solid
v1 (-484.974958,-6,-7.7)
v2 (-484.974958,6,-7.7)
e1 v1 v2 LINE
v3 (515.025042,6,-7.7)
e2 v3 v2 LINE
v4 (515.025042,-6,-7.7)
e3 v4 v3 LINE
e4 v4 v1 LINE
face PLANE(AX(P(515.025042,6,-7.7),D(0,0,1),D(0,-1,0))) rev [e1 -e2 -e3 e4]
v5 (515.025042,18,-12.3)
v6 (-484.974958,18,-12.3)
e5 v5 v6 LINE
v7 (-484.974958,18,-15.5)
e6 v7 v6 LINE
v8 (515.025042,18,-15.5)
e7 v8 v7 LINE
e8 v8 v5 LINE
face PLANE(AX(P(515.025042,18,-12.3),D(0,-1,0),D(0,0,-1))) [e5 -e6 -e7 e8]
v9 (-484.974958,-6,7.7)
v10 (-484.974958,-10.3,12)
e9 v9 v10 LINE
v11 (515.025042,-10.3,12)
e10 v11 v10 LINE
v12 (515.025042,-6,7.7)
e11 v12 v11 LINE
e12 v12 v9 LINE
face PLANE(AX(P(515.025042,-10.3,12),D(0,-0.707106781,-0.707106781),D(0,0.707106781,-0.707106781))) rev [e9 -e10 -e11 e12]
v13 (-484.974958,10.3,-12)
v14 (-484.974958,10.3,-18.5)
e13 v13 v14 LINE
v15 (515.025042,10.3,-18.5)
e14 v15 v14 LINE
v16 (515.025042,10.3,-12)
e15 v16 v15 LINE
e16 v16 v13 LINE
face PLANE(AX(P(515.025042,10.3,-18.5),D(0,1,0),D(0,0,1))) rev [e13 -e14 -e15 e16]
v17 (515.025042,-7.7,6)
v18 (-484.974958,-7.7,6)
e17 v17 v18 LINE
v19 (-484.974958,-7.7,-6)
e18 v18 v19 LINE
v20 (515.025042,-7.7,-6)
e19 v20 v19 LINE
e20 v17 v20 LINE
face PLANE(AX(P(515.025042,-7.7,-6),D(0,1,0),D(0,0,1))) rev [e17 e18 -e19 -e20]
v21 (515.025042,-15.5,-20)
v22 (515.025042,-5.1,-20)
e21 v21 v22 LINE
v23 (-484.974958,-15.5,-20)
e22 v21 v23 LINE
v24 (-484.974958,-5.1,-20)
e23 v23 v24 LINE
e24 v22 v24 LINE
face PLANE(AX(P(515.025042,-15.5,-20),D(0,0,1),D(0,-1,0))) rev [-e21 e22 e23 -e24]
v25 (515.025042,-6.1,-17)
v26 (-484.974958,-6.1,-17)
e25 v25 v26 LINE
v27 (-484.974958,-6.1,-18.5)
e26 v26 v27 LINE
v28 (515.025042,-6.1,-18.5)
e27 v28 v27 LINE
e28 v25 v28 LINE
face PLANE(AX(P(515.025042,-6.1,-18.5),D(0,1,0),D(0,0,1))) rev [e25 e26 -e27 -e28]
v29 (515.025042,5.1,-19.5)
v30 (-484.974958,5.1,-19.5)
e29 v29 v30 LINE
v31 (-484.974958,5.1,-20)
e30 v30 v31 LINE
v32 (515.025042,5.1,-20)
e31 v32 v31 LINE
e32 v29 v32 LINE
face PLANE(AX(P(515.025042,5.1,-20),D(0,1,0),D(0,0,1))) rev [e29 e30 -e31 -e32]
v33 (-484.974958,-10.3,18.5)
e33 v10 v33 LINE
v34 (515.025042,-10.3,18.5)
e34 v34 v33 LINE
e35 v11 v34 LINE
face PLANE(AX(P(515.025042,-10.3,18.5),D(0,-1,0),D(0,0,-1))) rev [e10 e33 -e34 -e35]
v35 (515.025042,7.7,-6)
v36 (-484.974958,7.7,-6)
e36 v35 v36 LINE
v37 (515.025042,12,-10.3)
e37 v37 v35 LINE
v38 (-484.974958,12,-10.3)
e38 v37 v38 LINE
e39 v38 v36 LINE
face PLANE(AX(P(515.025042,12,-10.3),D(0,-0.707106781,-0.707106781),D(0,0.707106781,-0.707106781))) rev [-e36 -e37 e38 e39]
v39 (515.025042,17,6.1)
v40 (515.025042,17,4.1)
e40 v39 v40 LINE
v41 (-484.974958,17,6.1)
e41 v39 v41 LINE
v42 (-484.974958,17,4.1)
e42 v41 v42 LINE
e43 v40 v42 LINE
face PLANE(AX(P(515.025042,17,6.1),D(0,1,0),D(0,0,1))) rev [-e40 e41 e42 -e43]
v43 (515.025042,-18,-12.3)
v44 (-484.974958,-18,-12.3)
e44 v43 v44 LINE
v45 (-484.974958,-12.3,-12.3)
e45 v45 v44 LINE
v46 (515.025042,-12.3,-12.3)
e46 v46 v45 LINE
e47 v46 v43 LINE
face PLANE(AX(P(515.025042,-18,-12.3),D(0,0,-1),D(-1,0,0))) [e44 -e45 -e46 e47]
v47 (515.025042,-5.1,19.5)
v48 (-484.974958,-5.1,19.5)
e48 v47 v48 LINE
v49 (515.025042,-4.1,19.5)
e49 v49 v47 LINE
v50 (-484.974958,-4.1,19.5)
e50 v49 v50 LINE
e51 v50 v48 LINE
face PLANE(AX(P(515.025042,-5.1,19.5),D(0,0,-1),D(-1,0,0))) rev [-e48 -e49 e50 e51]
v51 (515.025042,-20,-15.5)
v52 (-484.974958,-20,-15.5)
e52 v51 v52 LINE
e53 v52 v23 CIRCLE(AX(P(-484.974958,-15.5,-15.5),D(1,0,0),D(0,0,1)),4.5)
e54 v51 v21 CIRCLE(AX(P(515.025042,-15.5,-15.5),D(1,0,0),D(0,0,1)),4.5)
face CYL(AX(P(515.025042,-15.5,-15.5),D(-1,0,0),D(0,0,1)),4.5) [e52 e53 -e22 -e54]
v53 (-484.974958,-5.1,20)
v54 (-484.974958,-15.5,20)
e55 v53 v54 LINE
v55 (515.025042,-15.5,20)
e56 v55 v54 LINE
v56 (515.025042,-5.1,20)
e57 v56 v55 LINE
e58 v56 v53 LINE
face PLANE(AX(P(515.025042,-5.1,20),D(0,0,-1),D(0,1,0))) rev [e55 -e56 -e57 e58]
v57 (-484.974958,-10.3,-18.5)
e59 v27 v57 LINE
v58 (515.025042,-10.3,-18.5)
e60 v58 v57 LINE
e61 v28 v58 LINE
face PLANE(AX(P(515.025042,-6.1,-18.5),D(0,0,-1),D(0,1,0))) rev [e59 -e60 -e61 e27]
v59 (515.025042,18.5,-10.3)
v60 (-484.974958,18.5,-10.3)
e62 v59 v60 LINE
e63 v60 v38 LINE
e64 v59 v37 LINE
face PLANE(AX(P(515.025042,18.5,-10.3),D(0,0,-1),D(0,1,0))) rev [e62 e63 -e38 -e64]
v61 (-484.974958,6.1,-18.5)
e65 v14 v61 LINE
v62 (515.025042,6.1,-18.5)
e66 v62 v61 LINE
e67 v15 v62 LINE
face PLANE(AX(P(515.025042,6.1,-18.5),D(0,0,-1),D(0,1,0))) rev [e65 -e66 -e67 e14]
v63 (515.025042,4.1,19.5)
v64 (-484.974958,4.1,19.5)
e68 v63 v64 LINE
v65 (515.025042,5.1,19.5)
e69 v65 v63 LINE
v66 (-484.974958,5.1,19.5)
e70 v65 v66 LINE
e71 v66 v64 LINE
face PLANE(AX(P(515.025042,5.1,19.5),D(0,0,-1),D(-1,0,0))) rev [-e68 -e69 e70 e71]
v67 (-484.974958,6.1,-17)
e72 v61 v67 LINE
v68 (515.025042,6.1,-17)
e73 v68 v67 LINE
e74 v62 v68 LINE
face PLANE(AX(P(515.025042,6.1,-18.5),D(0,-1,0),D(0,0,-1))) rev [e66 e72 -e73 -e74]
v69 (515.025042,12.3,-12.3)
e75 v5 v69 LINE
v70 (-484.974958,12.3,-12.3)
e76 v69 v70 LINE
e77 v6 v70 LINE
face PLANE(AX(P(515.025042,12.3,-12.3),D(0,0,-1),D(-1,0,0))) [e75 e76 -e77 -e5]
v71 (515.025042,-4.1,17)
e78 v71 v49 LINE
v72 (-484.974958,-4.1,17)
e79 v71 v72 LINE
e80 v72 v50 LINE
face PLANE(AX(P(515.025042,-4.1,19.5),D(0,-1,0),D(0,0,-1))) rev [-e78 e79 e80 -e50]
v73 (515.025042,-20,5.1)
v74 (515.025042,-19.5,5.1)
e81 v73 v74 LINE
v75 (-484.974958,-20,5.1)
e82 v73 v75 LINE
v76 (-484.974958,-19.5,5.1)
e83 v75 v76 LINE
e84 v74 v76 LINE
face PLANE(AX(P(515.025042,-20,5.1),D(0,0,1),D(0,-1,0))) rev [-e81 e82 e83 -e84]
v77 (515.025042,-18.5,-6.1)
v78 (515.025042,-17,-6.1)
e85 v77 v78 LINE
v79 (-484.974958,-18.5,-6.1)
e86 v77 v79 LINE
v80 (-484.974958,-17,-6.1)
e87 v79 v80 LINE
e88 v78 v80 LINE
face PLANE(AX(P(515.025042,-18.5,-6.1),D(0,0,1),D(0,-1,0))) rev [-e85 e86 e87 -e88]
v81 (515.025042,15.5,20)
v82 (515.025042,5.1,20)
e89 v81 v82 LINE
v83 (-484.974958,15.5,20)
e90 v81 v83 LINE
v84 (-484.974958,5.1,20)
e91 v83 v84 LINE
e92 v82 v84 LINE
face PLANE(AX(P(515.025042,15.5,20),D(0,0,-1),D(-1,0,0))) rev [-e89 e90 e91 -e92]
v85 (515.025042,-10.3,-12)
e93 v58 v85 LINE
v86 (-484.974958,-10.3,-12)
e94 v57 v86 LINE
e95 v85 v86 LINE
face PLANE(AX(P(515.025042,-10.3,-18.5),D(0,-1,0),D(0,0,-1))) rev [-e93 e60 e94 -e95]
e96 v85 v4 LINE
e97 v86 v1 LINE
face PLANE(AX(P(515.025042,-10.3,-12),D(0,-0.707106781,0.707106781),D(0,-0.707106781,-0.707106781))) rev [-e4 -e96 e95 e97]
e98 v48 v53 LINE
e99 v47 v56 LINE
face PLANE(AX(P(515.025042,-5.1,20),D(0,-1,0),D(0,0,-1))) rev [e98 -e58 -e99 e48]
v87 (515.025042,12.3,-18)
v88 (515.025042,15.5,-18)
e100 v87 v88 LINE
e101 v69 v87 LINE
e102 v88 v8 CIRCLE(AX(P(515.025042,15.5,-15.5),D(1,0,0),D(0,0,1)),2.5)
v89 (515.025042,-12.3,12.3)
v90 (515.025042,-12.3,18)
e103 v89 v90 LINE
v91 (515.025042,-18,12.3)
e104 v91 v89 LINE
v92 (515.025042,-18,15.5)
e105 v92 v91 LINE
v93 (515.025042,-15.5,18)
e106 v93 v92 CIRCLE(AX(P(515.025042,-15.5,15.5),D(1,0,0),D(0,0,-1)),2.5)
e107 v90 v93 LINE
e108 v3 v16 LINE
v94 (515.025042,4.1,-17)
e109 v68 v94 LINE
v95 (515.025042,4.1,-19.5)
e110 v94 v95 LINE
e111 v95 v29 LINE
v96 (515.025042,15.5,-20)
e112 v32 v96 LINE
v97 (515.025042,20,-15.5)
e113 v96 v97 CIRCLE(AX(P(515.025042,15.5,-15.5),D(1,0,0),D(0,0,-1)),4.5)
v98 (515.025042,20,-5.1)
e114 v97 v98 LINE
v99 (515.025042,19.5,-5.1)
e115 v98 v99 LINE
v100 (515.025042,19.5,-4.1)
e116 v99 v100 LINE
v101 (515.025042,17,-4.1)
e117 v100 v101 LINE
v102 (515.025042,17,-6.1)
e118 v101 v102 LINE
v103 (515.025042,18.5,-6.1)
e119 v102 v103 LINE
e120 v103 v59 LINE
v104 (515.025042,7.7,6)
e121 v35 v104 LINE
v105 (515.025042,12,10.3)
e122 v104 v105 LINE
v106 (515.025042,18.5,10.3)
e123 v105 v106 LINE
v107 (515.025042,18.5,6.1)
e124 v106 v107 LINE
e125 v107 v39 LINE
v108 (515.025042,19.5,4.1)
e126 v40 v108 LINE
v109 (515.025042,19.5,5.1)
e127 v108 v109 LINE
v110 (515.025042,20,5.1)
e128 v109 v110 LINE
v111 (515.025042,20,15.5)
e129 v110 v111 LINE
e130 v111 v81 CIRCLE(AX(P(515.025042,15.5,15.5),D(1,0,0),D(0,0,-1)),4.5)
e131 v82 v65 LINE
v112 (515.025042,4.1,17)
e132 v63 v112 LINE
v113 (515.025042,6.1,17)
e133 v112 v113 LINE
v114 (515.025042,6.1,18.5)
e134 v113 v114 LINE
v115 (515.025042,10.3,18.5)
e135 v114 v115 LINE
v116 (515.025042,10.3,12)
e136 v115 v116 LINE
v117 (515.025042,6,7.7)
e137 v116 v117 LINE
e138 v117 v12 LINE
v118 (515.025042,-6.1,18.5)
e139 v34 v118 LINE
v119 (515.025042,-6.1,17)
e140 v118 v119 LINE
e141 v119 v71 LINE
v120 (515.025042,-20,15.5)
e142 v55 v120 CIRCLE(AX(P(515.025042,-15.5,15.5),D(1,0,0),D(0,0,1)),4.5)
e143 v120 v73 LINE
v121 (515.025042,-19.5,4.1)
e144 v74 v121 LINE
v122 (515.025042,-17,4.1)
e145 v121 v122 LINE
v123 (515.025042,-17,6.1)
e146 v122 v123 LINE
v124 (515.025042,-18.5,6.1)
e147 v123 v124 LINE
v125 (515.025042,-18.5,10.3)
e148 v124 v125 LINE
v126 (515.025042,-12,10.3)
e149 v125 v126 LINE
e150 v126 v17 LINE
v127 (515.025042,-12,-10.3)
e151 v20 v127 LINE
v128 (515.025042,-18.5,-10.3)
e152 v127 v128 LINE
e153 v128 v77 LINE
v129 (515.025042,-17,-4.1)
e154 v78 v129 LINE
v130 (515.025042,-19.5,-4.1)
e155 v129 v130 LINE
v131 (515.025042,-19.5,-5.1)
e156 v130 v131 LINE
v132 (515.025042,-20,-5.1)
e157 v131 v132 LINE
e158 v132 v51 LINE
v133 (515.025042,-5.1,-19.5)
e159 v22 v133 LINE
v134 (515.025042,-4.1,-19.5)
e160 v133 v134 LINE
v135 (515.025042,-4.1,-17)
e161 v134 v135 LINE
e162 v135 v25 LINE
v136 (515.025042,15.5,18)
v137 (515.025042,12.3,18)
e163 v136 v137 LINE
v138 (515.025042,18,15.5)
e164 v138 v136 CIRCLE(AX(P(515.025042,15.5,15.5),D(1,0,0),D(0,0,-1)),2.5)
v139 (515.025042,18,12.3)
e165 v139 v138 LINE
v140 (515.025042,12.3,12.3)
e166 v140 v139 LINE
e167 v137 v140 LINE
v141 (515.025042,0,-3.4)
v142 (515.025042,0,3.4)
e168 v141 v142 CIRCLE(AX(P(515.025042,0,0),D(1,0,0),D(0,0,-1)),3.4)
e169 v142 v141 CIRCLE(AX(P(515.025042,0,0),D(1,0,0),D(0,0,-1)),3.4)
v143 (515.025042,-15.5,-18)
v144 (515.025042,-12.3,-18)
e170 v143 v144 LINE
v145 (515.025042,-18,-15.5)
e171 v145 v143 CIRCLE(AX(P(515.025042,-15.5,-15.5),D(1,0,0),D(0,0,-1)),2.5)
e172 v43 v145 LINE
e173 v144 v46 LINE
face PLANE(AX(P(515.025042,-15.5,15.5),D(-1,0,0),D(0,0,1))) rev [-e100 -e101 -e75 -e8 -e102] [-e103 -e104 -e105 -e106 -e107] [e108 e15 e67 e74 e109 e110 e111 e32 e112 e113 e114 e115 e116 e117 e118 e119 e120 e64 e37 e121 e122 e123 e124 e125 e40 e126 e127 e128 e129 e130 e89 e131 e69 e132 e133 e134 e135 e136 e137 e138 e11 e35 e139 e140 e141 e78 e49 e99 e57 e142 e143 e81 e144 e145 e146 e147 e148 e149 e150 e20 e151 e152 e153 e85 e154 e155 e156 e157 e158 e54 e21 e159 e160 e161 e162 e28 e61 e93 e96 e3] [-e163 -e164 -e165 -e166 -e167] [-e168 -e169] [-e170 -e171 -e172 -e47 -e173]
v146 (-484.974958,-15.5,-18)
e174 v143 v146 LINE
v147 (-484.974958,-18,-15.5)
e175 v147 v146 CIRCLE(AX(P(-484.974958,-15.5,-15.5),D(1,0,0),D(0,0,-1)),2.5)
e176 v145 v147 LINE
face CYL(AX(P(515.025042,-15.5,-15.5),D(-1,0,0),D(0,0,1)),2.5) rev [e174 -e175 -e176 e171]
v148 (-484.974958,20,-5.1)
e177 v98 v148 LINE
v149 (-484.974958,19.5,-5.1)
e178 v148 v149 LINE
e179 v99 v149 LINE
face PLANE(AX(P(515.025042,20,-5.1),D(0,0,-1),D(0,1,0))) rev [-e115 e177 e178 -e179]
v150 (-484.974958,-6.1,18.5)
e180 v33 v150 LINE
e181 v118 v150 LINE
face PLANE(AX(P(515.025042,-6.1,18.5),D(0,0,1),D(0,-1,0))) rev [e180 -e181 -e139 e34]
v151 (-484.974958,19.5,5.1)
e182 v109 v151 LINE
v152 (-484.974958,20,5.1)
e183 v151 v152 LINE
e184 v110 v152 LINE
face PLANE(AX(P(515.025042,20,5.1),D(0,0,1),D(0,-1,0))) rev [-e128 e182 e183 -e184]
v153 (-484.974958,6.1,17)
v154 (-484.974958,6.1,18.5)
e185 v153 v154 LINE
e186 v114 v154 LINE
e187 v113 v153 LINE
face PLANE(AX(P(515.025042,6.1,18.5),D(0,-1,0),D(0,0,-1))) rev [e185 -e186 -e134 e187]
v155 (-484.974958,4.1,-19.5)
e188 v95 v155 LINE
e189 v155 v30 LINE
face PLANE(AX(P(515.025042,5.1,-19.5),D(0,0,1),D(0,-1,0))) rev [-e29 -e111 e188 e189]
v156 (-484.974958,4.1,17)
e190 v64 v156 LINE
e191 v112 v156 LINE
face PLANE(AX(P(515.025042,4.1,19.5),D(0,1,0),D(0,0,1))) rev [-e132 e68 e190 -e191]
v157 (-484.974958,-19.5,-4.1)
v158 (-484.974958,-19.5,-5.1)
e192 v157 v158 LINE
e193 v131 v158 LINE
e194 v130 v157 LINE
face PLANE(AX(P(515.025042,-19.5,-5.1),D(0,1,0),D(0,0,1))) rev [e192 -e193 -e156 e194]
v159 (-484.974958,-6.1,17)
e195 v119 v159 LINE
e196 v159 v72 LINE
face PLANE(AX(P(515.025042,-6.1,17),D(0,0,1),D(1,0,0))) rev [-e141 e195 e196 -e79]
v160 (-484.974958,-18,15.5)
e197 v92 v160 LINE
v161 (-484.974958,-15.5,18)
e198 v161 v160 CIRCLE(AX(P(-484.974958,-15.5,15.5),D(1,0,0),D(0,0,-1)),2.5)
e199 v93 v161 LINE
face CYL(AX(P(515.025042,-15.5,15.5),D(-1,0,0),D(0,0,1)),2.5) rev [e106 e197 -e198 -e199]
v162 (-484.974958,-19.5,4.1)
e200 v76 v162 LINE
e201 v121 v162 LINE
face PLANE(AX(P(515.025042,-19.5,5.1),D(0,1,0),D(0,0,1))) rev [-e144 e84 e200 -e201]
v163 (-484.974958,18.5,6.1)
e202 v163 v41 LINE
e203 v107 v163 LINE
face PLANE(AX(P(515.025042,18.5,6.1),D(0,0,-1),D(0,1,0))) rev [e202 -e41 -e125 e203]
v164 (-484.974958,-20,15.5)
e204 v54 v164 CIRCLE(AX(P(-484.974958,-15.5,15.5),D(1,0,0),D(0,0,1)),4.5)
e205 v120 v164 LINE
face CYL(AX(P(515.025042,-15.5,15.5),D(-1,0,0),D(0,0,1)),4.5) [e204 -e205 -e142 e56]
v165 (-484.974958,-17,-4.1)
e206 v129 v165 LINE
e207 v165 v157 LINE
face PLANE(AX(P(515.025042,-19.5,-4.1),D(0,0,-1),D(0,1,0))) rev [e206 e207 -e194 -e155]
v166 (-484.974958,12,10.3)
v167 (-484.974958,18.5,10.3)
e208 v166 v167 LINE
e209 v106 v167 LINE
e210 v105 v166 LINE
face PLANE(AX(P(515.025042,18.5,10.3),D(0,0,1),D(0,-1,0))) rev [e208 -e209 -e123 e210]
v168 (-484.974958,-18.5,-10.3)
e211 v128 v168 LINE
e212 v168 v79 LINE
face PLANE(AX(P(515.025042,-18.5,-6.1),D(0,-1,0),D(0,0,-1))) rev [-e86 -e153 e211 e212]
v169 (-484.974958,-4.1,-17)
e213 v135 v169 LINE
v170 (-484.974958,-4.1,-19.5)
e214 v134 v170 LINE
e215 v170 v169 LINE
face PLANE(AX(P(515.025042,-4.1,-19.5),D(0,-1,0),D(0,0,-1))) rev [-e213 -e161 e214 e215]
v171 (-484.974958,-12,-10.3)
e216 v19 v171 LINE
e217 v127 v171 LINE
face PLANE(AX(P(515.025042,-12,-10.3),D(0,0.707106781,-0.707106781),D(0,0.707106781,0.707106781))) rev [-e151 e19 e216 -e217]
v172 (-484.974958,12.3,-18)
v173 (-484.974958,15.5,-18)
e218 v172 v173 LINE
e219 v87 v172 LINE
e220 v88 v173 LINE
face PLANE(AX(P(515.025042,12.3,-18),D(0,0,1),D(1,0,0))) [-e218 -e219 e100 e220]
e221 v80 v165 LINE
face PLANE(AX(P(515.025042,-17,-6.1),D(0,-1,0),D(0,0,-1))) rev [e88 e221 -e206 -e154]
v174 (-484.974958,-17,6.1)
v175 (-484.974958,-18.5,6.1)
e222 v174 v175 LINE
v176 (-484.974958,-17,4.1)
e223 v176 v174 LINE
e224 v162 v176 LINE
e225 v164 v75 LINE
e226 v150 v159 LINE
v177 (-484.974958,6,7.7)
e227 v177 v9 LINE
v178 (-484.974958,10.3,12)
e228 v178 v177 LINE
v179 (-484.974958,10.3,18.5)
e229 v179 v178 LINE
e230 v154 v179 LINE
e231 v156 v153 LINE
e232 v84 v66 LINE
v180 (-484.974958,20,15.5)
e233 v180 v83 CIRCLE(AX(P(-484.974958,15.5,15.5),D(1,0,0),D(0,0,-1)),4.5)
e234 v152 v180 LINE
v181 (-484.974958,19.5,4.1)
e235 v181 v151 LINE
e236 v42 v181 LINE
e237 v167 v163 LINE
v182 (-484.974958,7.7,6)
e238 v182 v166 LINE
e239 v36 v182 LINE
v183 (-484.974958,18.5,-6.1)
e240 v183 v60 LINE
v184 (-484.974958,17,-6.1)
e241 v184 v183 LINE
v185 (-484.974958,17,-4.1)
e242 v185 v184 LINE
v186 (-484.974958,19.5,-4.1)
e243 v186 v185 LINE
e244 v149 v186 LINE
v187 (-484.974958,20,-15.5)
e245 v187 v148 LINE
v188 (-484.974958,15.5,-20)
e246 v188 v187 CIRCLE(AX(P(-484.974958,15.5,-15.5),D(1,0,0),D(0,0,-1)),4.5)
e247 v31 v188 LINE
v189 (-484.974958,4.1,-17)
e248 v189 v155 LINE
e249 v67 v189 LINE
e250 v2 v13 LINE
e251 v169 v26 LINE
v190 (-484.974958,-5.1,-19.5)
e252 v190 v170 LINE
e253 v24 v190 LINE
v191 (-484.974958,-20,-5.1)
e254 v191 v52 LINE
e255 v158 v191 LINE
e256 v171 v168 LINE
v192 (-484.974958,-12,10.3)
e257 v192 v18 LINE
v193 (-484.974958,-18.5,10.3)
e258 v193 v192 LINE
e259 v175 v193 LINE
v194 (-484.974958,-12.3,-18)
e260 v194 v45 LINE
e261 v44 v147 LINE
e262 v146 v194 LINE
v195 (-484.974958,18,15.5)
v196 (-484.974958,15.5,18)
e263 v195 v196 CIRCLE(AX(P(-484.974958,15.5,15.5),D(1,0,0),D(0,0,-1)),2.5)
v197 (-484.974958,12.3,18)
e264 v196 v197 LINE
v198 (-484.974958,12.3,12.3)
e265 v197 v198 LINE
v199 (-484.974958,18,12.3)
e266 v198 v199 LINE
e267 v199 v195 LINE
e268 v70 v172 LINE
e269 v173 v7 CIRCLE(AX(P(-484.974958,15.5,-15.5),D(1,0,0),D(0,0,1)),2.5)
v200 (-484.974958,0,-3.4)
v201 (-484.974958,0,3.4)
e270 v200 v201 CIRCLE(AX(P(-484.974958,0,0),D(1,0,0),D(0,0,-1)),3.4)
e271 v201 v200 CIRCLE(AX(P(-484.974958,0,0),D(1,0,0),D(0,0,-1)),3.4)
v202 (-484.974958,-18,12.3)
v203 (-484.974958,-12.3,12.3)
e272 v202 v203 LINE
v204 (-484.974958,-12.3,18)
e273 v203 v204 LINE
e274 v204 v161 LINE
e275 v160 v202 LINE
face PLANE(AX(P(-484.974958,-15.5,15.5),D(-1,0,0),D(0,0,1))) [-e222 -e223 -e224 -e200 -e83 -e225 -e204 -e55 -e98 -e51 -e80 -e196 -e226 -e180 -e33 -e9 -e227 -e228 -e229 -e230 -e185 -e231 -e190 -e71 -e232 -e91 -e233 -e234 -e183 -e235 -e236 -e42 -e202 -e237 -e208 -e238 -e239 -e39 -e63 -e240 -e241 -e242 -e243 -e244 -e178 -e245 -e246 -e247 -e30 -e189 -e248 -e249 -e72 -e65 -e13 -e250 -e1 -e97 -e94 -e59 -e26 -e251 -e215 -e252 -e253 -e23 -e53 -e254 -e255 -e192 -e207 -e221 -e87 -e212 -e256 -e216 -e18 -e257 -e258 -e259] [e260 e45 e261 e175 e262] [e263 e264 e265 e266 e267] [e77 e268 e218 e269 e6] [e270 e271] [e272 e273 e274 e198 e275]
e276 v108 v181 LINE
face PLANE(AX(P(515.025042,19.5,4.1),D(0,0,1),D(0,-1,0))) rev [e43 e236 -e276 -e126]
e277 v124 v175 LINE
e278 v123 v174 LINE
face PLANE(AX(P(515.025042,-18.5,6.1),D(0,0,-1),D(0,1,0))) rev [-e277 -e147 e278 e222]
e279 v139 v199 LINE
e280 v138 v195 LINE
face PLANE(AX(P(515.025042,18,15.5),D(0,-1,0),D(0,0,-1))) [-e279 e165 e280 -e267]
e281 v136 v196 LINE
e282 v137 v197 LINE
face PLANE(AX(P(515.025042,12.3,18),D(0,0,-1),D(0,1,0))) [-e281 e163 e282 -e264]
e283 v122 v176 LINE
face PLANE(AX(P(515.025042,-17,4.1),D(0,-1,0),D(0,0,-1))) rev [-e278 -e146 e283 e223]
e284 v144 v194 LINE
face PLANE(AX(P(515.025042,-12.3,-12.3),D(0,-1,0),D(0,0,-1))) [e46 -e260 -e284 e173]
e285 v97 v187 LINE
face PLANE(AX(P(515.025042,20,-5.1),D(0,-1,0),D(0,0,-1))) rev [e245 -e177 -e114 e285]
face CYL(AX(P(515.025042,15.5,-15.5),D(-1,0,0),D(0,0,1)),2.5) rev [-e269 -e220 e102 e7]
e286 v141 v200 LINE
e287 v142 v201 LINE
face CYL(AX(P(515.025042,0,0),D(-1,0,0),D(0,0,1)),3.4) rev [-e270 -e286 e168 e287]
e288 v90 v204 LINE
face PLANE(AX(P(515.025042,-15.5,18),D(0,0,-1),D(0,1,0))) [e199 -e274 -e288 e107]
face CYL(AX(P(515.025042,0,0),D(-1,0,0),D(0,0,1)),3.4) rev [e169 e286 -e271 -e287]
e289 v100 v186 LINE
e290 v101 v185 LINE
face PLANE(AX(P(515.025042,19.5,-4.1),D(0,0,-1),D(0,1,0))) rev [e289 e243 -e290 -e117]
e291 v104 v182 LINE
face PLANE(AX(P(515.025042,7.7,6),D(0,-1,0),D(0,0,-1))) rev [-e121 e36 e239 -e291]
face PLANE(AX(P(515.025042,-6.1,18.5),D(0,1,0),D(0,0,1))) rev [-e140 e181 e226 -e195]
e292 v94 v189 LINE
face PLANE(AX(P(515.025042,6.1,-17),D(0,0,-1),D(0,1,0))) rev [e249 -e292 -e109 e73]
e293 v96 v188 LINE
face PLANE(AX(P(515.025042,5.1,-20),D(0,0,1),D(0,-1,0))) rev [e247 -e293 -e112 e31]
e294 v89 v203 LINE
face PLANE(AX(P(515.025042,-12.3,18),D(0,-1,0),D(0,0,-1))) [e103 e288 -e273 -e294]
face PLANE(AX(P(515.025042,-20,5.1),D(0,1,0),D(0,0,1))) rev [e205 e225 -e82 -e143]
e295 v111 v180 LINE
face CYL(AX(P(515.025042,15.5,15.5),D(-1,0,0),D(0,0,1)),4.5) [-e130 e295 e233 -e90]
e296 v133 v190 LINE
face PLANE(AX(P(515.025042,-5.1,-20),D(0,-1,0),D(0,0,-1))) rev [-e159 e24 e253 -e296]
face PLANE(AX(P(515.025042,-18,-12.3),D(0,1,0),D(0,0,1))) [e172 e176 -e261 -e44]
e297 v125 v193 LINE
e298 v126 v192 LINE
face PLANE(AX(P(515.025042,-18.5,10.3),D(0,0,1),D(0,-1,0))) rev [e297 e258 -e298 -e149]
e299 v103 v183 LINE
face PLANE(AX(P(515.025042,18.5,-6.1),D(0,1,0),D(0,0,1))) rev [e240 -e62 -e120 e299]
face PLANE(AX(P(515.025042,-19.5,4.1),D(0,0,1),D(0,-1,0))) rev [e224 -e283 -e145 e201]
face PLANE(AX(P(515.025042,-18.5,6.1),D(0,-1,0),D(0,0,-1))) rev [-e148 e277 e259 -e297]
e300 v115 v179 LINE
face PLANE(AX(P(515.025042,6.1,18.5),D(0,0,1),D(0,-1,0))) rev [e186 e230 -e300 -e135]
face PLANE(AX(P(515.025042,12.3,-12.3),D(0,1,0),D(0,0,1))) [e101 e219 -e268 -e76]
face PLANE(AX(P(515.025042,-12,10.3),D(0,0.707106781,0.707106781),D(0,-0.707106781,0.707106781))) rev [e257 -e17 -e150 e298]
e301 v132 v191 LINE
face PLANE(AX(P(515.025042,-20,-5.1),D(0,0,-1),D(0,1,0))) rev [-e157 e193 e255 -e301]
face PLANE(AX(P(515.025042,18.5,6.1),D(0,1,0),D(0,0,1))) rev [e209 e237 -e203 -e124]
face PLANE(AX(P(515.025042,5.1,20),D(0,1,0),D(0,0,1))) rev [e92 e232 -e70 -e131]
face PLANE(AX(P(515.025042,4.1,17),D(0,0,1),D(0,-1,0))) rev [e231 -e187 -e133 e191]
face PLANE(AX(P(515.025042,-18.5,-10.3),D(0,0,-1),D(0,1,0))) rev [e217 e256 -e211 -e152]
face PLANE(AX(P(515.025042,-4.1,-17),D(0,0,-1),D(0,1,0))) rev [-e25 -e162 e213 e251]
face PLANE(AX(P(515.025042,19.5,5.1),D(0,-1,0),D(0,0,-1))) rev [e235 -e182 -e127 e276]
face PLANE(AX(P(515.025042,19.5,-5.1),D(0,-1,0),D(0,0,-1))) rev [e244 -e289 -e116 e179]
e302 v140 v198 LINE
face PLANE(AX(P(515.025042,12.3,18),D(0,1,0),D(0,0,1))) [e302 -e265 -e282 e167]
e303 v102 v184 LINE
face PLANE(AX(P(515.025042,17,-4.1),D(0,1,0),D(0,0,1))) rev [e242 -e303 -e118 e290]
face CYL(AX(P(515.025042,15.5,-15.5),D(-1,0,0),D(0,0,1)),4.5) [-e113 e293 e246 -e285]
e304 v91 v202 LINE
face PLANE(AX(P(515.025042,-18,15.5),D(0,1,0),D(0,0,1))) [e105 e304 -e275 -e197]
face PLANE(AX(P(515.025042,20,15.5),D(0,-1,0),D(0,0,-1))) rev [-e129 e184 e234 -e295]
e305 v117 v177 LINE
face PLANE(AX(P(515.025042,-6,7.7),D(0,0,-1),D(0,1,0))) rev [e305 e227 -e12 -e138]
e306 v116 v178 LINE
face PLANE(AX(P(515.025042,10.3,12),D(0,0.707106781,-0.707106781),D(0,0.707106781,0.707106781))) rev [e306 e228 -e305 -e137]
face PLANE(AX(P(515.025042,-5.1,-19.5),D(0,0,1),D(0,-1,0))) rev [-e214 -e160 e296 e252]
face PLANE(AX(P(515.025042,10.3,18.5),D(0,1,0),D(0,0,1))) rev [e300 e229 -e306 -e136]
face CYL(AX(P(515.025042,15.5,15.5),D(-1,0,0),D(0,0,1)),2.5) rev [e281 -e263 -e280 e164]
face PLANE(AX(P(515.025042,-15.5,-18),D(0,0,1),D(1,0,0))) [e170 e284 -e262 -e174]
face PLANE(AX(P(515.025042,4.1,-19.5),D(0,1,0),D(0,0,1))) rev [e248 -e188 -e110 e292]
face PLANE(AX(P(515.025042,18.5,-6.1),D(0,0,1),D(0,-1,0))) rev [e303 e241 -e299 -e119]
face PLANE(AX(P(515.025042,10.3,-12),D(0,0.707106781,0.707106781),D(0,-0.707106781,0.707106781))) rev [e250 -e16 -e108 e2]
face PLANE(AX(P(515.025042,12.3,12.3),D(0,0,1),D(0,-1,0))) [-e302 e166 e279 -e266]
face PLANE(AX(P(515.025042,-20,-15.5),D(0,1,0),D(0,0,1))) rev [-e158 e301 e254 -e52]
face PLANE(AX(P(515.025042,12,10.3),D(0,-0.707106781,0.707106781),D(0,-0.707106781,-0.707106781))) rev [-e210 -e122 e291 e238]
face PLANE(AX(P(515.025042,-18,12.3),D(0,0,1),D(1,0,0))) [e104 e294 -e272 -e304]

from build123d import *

# Parameters (mm, degrees)
SKETCH1_R                                 = 3.4
ALUMINIUM_PROFILE_40_X_40B_X_R4_5_1_DEPTH = 1000


with BuildPart() as part:
    # Sketch1 → Aluminium profile 40 X 40B X R4.5(1) (new body)
    with BuildSketch(Plane.YZ.offset(-484.974958264)):
        with BuildLine():
            Line((-5.1, 20), (-5.1, 19.5))
            Line((-5.1, 19.5), (-4.1, 19.5))
            Line((-4.1, 19.5), (-4.1, 17))
            Line((-4.1, 17), (-6.1, 17))
            Line((-6.1, 17), (-6.1, 18.5))
            Line((-6.1, 18.5), (-10.3, 18.5))
            Line((-10.3, 18.5), (-10.3, 12))
            Line((-10.3, 12), (-6, 7.7))
            Line((-6, 7.7), (6, 7.7))
            Line((6, 7.7), (10.3, 12))
            Line((10.3, 12), (10.3, 18.5))
            Line((10.3, 18.5), (6.1, 18.5))
            Line((6.1, 18.5), (6.1, 17))
            Line((6.1, 17), (4.1, 17))
            Line((4.1, 17), (4.1, 19.5))
            Line((4.1, 19.5), (5.1, 19.5))
            Line((5.1, 19.5), (5.1, 20))
            Line((5.1, 20), (15.5, 20))
            ThreePointArc((15.5, 20), (18.681980515, 18.681980515), (20, 15.5))
            Line((20, 15.5), (20, 5.1))
            Line((20, 5.1), (19.5, 5.1))
            Line((19.5, 5.1), (19.5, 4.1))
            Line((19.5, 4.1), (17, 4.1))
            Line((17, 4.1), (17, 6.1))
            Line((17, 6.1), (18.5, 6.1))
            Line((18.5, 6.1), (18.5, 10.3))
            Line((18.5, 10.3), (12, 10.3))
            Line((12, 10.3), (7.7, 6))
            Line((7.7, 6), (7.7, -6))
            Line((7.7, -6), (12, -10.3))
            Line((12, -10.3), (18.5, -10.3))
            Line((18.5, -10.3), (18.5, -6.1))
            Line((18.5, -6.1), (17, -6.1))
            Line((17, -6.1), (17, -4.1))
            Line((17, -4.1), (19.5, -4.1))
            Line((19.5, -4.1), (19.5, -5.1))
            Line((19.5, -5.1), (20, -5.1))
            Line((20, -5.1), (20, -15.5))
            ThreePointArc((20, -15.5), (18.681980515, -18.681980515), (15.5, -20))
            Line((15.5, -20), (5.1, -20))
            Line((5.1, -20), (5.1, -19.5))
            Line((5.1, -19.5), (4.1, -19.5))
            Line((4.1, -19.5), (4.1, -17))
            Line((4.1, -17), (6.1, -17))
            Line((6.1, -17), (6.1, -18.5))
            Line((6.1, -18.5), (10.3, -18.5))
            Line((10.3, -18.5), (10.3, -12))
            Line((10.3, -12), (6, -7.7))
            Line((6, -7.7), (-6, -7.7))
            Line((-6, -7.7), (-10.3, -12))
            Line((-10.3, -12), (-10.3, -18.5))
            Line((-10.3, -18.5), (-6.1, -18.5))
            Line((-6.1, -18.5), (-6.1, -17))
            Line((-6.1, -17), (-4.1, -17))
            Line((-4.1, -17), (-4.1, -19.5))
            Line((-4.1, -19.5), (-5.1, -19.5))
            Line((-5.1, -19.5), (-5.1, -20))
            Line((-5.1, -20), (-15.5, -20))
            ThreePointArc((-15.5, -20), (-18.681980515, -18.681980515), (-20, -15.5))
            Line((-20, -15.5), (-20, -5.1))
            Line((-20, -5.1), (-19.5, -5.1))
            Line((-19.5, -5.1), (-19.5, -4.1))
            Line((-19.5, -4.1), (-17, -4.1))
            Line((-17, -4.1), (-17, -6.1))
            Line((-17, -6.1), (-18.5, -6.1))
            Line((-18.5, -6.1), (-18.5, -10.3))
            Line((-18.5, -10.3), (-12, -10.3))
            Line((-12, -10.3), (-7.7, -6))
            Line((-7.7, -6), (-7.7, 6))
            Line((-7.7, 6), (-12, 10.3))
            Line((-12, 10.3), (-18.5, 10.3))
            Line((-18.5, 10.3), (-18.5, 6.1))
            Line((-18.5, 6.1), (-17, 6.1))
            Line((-17, 6.1), (-17, 4.1))
            Line((-17, 4.1), (-19.5, 4.1))
            Line((-19.5, 4.1), (-19.5, 5.1))
            Line((-19.5, 5.1), (-20, 5.1))
            Line((-20, 5.1), (-20, 15.5))
            ThreePointArc((-20, 15.5), (-18.681980515, 18.681980515), (-15.5, 20))
            Line((-15.5, 20), (-5.1, 20))
        make_face()
        Circle(SKETCH1_R, mode=Mode.SUBTRACT)
        with BuildLine():
            Line((12.3, 18), (15.5, 18))
            ThreePointArc((15.5, 18), (17.267766953, 17.267766953), (18, 15.5))
            Line((18, 15.5), (18, 12.3))
            Line((18, 12.3), (12.3, 12.3))
            Line((12.3, 12.3), (12.3, 18))
        make_face(mode=Mode.SUBTRACT)
        with BuildLine():
            Line((-15.5, 18), (-12.3, 18))
            Line((-12.3, 18), (-12.3, 12.3))
            Line((-12.3, 12.3), (-18, 12.3))
            Line((-18, 12.3), (-18, 15.5))
            ThreePointArc((-18, 15.5), (-17.267766953, 17.267766953), (-15.5, 18))
        make_face(mode=Mode.SUBTRACT)
        with BuildLine():
            Line((-18, -12.3), (-12.3, -12.3))
            Line((-12.3, -12.3), (-12.3, -18))
            Line((-12.3, -18), (-15.5, -18))
            ThreePointArc((-15.5, -18), (-17.267766953, -17.267766953), (-18, -15.5))
            Line((-18, -15.5), (-18, -12.3))
        make_face(mode=Mode.SUBTRACT)
        with BuildLine():
            Line((12.3, -12.3), (18, -12.3))
            Line((18, -12.3), (18, -15.5))
            ThreePointArc((18, -15.5), (17.267766953, -17.267766953), (15.5, -18))
            Line((15.5, -18), (12.3, -18))
            Line((12.3, -18), (12.3, -12.3))
        make_face(mode=Mode.SUBTRACT)
    extrude(amount=ALUMINIUM_PROFILE_40_X_40B_X_R4_5_1_DEPTH)


solid = part.part
